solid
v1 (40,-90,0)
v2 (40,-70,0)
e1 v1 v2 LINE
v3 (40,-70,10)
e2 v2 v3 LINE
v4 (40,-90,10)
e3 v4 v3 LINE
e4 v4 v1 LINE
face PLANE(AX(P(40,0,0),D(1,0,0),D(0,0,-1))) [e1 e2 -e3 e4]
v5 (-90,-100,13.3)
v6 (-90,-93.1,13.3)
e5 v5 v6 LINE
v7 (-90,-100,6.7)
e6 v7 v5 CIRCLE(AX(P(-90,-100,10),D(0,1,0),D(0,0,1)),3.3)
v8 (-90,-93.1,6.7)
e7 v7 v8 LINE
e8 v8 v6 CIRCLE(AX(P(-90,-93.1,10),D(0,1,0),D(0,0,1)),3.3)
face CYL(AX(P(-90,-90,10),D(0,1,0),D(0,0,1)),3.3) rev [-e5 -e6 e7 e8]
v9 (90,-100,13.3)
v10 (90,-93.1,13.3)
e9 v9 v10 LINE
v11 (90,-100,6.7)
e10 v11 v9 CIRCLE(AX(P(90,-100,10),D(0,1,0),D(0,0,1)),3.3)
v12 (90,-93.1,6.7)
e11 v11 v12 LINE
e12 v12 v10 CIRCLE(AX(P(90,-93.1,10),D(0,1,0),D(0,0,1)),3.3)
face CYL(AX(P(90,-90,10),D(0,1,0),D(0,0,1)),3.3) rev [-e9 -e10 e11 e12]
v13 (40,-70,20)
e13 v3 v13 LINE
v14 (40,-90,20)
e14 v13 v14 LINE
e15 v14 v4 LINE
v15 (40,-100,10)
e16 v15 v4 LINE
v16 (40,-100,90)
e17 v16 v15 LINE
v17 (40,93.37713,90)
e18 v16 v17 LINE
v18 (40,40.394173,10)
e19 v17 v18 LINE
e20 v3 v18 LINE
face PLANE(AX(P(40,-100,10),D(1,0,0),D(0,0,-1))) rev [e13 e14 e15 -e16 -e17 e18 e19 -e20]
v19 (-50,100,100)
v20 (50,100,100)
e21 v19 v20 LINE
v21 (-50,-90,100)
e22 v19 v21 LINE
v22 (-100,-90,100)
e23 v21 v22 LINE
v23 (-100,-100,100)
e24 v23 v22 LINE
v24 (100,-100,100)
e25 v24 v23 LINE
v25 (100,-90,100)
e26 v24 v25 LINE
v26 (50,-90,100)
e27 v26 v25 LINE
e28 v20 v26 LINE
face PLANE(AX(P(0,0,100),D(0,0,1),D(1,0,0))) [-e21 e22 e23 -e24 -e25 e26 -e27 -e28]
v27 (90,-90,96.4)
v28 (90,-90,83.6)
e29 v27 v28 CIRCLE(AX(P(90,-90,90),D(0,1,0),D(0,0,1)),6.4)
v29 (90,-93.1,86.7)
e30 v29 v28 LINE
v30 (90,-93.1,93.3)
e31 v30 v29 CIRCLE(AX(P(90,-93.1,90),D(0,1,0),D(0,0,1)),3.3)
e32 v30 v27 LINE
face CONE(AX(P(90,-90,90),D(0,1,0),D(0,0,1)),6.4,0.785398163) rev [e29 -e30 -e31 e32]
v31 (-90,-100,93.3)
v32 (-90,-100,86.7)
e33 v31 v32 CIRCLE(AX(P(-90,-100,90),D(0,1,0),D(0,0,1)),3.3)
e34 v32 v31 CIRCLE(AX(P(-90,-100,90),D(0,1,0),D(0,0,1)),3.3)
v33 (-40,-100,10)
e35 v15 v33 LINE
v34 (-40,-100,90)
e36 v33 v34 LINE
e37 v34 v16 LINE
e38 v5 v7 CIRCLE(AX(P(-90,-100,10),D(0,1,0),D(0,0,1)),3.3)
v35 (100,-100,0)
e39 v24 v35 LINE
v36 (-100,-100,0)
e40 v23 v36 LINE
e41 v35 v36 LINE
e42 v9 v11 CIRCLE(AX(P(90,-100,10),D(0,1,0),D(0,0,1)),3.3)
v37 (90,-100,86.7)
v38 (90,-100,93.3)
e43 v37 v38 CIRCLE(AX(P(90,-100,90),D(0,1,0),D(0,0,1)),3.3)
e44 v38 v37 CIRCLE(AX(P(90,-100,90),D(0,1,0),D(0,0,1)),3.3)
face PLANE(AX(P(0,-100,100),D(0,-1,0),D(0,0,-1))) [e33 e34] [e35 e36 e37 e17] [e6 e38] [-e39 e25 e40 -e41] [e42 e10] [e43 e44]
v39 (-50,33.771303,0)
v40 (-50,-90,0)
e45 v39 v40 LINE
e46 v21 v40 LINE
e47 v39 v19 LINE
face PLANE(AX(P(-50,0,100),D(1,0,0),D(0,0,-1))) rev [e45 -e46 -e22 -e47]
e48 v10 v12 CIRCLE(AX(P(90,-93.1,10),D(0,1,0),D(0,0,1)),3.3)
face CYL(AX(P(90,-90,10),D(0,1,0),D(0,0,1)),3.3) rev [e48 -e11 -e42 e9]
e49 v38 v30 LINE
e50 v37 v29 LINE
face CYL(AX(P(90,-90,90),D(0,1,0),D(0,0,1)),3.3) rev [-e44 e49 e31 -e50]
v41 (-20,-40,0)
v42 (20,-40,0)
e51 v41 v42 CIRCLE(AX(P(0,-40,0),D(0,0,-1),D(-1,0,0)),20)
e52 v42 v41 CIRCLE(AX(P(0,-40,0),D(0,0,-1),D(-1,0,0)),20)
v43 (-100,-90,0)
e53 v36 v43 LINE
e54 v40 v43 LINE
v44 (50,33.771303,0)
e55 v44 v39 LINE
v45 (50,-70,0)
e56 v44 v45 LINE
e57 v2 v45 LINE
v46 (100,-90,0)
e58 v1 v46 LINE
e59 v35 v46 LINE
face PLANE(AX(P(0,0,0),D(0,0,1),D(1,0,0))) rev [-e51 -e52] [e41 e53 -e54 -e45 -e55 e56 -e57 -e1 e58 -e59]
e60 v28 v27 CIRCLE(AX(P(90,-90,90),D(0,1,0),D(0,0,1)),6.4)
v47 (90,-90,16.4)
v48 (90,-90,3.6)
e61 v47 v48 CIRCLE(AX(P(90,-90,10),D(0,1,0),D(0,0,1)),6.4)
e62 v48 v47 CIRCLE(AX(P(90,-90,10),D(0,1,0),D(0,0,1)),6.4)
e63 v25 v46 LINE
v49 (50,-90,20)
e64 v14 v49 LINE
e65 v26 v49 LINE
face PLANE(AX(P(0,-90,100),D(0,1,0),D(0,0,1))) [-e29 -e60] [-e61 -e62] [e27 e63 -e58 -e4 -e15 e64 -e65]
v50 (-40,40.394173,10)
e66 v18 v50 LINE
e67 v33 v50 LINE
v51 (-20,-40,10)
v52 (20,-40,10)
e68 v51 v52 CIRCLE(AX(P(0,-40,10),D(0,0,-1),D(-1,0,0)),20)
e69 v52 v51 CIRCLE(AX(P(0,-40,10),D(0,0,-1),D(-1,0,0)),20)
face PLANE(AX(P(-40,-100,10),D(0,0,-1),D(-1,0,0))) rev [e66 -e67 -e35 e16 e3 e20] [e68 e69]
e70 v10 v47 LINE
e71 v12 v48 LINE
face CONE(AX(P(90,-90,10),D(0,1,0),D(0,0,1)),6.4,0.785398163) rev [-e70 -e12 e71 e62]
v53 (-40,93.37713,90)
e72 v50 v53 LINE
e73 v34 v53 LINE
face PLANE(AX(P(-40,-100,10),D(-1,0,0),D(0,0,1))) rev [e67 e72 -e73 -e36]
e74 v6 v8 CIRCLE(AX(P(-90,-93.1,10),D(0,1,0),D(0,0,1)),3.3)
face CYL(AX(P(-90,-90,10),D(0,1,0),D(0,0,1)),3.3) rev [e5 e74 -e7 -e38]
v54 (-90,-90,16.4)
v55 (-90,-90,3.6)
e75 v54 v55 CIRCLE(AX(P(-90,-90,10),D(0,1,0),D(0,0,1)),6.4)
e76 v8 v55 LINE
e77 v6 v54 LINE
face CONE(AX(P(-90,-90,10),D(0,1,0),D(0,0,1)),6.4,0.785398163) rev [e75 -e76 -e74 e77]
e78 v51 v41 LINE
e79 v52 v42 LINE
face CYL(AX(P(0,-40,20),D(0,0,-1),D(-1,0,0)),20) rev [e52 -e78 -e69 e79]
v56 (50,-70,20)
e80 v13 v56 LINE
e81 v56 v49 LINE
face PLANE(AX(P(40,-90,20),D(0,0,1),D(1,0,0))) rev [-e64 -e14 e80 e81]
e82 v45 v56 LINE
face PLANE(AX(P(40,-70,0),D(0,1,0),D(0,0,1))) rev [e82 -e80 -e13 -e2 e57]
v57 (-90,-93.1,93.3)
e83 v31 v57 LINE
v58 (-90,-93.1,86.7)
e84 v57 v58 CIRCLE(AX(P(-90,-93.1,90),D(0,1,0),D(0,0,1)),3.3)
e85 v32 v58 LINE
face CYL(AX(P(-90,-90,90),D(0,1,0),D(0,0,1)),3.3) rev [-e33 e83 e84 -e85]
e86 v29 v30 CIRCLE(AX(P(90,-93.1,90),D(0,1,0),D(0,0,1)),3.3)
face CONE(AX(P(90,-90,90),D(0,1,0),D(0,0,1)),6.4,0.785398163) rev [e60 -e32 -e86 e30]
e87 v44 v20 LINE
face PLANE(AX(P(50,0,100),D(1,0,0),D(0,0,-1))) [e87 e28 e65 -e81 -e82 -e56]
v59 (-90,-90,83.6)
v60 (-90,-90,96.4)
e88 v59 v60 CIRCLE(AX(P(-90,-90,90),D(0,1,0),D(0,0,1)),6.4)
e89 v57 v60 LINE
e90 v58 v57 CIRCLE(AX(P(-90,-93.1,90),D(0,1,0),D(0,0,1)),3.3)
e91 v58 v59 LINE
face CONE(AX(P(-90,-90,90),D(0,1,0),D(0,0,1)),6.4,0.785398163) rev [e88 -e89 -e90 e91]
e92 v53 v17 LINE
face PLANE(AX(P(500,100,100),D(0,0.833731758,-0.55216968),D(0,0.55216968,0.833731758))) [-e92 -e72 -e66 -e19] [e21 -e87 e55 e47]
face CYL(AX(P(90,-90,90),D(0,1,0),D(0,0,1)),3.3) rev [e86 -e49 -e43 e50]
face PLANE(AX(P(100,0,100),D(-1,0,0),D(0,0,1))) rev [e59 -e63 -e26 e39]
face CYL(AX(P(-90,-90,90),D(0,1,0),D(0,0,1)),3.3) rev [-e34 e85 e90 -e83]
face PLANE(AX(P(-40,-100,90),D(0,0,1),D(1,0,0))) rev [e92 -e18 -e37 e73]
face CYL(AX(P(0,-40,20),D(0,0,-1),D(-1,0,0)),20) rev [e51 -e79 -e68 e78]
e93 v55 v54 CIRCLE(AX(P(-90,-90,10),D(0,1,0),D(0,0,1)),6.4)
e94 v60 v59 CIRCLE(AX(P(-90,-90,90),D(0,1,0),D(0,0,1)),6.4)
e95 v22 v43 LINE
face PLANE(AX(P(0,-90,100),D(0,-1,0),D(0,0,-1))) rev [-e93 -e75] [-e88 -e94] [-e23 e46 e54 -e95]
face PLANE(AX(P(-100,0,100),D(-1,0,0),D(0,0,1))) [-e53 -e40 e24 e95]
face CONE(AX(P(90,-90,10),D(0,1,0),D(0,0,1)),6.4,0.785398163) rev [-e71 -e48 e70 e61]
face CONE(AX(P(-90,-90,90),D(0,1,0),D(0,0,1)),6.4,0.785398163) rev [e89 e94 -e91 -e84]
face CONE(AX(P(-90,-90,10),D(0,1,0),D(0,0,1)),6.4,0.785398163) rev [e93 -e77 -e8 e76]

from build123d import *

# Parameters (mm, degrees)
SKETCH1_W                                            = 50
SKETCH1_H                                            = 10
SKETCH1_W_2                                          = 100
SKETCH1_H_2                                          = 200
BOSS_EXTRUDE1_DEPTH                                  = 100
CUT_EXTRUDE1_DEPTH                                   = 174.205080757
CUT_EXTRUDE1_DEPTH_BACK                              = 174.205080757
SKETCH7_W                                            = 80
SKETCH7_H                                            = 80
CUT_EXTRUDE2_DEPTH                                   = 100
SKETCH8_R                                            = 20
CUT_EXTRUDE3_DEPTH                                   = 20
CSK_FOR_M6_HEXAGON_LOBULAR_SOCKET_RAISED_D           = 6.6
CSK_FOR_M6_HEXAGON_LOBULAR_SOCKET_RAISED_CSINK_D     = 12.8
CSK_FOR_M6_HEXAGON_LOBULAR_SOCKET_RAISED_CSINK_ANGLE = 90
SKETCH13_W                                           = 20
SKETCH13_H                                           = 20
CUT_EXTRUDE4_DEPTH                                   = 10


with BuildPart() as part:
    # Sketch1 → Boss-Extrude1 (new body)
    with BuildSketch(Plane.XY):
        with Locations((-75, -95)):
            Rectangle(SKETCH1_W, SKETCH1_H)
        Rectangle(SKETCH1_W_2, SKETCH1_H_2)
        with Locations((75, -95)):
            Rectangle(SKETCH1_W, SKETCH1_H)
    extrude(amount=BOSS_EXTRUDE1_DEPTH)

    # Sketch5 → Cut-Extrude1 (cut, two sides: drawn at the far end of the back side and taken through both)
    with BuildSketch(Plane(origin=(0, 0, 0), x_dir=(0, 0, -1), z_dir=(1, 0, 0)).offset(-CUT_EXTRUDE1_DEPTH_BACK)):
        Polygon((-481.193494813, 352.459484715), (-100, 100), (0, 33.771302986), (381.193494813, -218.688181728), (886.112464242, 543.698807897), (23.725474617, 1114.84647434), align=None)
    extrude(amount=CUT_EXTRUDE1_DEPTH + CUT_EXTRUDE1_DEPTH_BACK, mode=Mode.SUBTRACT)

    # Sketch7 → Cut-Extrude2 (cut, symmetric)
    with BuildSketch(Plane(origin=(0, 0, 0), x_dir=(1, 0, 0), z_dir=(0, 1, 0))):
        with Locations((0, -50)):
            Rectangle(SKETCH7_W, SKETCH7_H)
    extrude(amount=CUT_EXTRUDE2_DEPTH, both=True, mode=Mode.SUBTRACT)

    # Sketch8 → Cut-Extrude3 (cut)
    with BuildSketch(Plane(origin=(0, 0, 0), x_dir=(-1, 0, 0), z_dir=(0, 0, -1))):
        with Locations((0, -40)):
            Circle(SKETCH8_R)
    extrude(amount=-CUT_EXTRUDE3_DEPTH, mode=Mode.SUBTRACT)

    # CSK for M6 Hexagon lobular socket raised CTSK head screws1 (through all)
    with Locations(Plane(origin=(0, -90, 0), x_dir=(1, 0, 0), z_dir=(0, 1, 0))):
        with Locations((-90, -10), (-90, -90), (90, -10), (90, -90)):
            CounterSinkHole(CSK_FOR_M6_HEXAGON_LOBULAR_SOCKET_RAISED_D / 2, CSK_FOR_M6_HEXAGON_LOBULAR_SOCKET_RAISED_CSINK_D / 2, counter_sink_angle=CSK_FOR_M6_HEXAGON_LOBULAR_SOCKET_RAISED_CSINK_ANGLE)

    # Sketch13 → Cut-Extrude4 (cut)
    with BuildSketch(Plane(origin=(50, 0, 0), x_dir=(0, 0, -1), z_dir=(1, 0, 0))):
        with Locations((-10, -80)):
            Rectangle(SKETCH13_W, SKETCH13_H)
    extrude(amount=-CUT_EXTRUDE4_DEPTH, mode=Mode.SUBTRACT)


solid = part.part
